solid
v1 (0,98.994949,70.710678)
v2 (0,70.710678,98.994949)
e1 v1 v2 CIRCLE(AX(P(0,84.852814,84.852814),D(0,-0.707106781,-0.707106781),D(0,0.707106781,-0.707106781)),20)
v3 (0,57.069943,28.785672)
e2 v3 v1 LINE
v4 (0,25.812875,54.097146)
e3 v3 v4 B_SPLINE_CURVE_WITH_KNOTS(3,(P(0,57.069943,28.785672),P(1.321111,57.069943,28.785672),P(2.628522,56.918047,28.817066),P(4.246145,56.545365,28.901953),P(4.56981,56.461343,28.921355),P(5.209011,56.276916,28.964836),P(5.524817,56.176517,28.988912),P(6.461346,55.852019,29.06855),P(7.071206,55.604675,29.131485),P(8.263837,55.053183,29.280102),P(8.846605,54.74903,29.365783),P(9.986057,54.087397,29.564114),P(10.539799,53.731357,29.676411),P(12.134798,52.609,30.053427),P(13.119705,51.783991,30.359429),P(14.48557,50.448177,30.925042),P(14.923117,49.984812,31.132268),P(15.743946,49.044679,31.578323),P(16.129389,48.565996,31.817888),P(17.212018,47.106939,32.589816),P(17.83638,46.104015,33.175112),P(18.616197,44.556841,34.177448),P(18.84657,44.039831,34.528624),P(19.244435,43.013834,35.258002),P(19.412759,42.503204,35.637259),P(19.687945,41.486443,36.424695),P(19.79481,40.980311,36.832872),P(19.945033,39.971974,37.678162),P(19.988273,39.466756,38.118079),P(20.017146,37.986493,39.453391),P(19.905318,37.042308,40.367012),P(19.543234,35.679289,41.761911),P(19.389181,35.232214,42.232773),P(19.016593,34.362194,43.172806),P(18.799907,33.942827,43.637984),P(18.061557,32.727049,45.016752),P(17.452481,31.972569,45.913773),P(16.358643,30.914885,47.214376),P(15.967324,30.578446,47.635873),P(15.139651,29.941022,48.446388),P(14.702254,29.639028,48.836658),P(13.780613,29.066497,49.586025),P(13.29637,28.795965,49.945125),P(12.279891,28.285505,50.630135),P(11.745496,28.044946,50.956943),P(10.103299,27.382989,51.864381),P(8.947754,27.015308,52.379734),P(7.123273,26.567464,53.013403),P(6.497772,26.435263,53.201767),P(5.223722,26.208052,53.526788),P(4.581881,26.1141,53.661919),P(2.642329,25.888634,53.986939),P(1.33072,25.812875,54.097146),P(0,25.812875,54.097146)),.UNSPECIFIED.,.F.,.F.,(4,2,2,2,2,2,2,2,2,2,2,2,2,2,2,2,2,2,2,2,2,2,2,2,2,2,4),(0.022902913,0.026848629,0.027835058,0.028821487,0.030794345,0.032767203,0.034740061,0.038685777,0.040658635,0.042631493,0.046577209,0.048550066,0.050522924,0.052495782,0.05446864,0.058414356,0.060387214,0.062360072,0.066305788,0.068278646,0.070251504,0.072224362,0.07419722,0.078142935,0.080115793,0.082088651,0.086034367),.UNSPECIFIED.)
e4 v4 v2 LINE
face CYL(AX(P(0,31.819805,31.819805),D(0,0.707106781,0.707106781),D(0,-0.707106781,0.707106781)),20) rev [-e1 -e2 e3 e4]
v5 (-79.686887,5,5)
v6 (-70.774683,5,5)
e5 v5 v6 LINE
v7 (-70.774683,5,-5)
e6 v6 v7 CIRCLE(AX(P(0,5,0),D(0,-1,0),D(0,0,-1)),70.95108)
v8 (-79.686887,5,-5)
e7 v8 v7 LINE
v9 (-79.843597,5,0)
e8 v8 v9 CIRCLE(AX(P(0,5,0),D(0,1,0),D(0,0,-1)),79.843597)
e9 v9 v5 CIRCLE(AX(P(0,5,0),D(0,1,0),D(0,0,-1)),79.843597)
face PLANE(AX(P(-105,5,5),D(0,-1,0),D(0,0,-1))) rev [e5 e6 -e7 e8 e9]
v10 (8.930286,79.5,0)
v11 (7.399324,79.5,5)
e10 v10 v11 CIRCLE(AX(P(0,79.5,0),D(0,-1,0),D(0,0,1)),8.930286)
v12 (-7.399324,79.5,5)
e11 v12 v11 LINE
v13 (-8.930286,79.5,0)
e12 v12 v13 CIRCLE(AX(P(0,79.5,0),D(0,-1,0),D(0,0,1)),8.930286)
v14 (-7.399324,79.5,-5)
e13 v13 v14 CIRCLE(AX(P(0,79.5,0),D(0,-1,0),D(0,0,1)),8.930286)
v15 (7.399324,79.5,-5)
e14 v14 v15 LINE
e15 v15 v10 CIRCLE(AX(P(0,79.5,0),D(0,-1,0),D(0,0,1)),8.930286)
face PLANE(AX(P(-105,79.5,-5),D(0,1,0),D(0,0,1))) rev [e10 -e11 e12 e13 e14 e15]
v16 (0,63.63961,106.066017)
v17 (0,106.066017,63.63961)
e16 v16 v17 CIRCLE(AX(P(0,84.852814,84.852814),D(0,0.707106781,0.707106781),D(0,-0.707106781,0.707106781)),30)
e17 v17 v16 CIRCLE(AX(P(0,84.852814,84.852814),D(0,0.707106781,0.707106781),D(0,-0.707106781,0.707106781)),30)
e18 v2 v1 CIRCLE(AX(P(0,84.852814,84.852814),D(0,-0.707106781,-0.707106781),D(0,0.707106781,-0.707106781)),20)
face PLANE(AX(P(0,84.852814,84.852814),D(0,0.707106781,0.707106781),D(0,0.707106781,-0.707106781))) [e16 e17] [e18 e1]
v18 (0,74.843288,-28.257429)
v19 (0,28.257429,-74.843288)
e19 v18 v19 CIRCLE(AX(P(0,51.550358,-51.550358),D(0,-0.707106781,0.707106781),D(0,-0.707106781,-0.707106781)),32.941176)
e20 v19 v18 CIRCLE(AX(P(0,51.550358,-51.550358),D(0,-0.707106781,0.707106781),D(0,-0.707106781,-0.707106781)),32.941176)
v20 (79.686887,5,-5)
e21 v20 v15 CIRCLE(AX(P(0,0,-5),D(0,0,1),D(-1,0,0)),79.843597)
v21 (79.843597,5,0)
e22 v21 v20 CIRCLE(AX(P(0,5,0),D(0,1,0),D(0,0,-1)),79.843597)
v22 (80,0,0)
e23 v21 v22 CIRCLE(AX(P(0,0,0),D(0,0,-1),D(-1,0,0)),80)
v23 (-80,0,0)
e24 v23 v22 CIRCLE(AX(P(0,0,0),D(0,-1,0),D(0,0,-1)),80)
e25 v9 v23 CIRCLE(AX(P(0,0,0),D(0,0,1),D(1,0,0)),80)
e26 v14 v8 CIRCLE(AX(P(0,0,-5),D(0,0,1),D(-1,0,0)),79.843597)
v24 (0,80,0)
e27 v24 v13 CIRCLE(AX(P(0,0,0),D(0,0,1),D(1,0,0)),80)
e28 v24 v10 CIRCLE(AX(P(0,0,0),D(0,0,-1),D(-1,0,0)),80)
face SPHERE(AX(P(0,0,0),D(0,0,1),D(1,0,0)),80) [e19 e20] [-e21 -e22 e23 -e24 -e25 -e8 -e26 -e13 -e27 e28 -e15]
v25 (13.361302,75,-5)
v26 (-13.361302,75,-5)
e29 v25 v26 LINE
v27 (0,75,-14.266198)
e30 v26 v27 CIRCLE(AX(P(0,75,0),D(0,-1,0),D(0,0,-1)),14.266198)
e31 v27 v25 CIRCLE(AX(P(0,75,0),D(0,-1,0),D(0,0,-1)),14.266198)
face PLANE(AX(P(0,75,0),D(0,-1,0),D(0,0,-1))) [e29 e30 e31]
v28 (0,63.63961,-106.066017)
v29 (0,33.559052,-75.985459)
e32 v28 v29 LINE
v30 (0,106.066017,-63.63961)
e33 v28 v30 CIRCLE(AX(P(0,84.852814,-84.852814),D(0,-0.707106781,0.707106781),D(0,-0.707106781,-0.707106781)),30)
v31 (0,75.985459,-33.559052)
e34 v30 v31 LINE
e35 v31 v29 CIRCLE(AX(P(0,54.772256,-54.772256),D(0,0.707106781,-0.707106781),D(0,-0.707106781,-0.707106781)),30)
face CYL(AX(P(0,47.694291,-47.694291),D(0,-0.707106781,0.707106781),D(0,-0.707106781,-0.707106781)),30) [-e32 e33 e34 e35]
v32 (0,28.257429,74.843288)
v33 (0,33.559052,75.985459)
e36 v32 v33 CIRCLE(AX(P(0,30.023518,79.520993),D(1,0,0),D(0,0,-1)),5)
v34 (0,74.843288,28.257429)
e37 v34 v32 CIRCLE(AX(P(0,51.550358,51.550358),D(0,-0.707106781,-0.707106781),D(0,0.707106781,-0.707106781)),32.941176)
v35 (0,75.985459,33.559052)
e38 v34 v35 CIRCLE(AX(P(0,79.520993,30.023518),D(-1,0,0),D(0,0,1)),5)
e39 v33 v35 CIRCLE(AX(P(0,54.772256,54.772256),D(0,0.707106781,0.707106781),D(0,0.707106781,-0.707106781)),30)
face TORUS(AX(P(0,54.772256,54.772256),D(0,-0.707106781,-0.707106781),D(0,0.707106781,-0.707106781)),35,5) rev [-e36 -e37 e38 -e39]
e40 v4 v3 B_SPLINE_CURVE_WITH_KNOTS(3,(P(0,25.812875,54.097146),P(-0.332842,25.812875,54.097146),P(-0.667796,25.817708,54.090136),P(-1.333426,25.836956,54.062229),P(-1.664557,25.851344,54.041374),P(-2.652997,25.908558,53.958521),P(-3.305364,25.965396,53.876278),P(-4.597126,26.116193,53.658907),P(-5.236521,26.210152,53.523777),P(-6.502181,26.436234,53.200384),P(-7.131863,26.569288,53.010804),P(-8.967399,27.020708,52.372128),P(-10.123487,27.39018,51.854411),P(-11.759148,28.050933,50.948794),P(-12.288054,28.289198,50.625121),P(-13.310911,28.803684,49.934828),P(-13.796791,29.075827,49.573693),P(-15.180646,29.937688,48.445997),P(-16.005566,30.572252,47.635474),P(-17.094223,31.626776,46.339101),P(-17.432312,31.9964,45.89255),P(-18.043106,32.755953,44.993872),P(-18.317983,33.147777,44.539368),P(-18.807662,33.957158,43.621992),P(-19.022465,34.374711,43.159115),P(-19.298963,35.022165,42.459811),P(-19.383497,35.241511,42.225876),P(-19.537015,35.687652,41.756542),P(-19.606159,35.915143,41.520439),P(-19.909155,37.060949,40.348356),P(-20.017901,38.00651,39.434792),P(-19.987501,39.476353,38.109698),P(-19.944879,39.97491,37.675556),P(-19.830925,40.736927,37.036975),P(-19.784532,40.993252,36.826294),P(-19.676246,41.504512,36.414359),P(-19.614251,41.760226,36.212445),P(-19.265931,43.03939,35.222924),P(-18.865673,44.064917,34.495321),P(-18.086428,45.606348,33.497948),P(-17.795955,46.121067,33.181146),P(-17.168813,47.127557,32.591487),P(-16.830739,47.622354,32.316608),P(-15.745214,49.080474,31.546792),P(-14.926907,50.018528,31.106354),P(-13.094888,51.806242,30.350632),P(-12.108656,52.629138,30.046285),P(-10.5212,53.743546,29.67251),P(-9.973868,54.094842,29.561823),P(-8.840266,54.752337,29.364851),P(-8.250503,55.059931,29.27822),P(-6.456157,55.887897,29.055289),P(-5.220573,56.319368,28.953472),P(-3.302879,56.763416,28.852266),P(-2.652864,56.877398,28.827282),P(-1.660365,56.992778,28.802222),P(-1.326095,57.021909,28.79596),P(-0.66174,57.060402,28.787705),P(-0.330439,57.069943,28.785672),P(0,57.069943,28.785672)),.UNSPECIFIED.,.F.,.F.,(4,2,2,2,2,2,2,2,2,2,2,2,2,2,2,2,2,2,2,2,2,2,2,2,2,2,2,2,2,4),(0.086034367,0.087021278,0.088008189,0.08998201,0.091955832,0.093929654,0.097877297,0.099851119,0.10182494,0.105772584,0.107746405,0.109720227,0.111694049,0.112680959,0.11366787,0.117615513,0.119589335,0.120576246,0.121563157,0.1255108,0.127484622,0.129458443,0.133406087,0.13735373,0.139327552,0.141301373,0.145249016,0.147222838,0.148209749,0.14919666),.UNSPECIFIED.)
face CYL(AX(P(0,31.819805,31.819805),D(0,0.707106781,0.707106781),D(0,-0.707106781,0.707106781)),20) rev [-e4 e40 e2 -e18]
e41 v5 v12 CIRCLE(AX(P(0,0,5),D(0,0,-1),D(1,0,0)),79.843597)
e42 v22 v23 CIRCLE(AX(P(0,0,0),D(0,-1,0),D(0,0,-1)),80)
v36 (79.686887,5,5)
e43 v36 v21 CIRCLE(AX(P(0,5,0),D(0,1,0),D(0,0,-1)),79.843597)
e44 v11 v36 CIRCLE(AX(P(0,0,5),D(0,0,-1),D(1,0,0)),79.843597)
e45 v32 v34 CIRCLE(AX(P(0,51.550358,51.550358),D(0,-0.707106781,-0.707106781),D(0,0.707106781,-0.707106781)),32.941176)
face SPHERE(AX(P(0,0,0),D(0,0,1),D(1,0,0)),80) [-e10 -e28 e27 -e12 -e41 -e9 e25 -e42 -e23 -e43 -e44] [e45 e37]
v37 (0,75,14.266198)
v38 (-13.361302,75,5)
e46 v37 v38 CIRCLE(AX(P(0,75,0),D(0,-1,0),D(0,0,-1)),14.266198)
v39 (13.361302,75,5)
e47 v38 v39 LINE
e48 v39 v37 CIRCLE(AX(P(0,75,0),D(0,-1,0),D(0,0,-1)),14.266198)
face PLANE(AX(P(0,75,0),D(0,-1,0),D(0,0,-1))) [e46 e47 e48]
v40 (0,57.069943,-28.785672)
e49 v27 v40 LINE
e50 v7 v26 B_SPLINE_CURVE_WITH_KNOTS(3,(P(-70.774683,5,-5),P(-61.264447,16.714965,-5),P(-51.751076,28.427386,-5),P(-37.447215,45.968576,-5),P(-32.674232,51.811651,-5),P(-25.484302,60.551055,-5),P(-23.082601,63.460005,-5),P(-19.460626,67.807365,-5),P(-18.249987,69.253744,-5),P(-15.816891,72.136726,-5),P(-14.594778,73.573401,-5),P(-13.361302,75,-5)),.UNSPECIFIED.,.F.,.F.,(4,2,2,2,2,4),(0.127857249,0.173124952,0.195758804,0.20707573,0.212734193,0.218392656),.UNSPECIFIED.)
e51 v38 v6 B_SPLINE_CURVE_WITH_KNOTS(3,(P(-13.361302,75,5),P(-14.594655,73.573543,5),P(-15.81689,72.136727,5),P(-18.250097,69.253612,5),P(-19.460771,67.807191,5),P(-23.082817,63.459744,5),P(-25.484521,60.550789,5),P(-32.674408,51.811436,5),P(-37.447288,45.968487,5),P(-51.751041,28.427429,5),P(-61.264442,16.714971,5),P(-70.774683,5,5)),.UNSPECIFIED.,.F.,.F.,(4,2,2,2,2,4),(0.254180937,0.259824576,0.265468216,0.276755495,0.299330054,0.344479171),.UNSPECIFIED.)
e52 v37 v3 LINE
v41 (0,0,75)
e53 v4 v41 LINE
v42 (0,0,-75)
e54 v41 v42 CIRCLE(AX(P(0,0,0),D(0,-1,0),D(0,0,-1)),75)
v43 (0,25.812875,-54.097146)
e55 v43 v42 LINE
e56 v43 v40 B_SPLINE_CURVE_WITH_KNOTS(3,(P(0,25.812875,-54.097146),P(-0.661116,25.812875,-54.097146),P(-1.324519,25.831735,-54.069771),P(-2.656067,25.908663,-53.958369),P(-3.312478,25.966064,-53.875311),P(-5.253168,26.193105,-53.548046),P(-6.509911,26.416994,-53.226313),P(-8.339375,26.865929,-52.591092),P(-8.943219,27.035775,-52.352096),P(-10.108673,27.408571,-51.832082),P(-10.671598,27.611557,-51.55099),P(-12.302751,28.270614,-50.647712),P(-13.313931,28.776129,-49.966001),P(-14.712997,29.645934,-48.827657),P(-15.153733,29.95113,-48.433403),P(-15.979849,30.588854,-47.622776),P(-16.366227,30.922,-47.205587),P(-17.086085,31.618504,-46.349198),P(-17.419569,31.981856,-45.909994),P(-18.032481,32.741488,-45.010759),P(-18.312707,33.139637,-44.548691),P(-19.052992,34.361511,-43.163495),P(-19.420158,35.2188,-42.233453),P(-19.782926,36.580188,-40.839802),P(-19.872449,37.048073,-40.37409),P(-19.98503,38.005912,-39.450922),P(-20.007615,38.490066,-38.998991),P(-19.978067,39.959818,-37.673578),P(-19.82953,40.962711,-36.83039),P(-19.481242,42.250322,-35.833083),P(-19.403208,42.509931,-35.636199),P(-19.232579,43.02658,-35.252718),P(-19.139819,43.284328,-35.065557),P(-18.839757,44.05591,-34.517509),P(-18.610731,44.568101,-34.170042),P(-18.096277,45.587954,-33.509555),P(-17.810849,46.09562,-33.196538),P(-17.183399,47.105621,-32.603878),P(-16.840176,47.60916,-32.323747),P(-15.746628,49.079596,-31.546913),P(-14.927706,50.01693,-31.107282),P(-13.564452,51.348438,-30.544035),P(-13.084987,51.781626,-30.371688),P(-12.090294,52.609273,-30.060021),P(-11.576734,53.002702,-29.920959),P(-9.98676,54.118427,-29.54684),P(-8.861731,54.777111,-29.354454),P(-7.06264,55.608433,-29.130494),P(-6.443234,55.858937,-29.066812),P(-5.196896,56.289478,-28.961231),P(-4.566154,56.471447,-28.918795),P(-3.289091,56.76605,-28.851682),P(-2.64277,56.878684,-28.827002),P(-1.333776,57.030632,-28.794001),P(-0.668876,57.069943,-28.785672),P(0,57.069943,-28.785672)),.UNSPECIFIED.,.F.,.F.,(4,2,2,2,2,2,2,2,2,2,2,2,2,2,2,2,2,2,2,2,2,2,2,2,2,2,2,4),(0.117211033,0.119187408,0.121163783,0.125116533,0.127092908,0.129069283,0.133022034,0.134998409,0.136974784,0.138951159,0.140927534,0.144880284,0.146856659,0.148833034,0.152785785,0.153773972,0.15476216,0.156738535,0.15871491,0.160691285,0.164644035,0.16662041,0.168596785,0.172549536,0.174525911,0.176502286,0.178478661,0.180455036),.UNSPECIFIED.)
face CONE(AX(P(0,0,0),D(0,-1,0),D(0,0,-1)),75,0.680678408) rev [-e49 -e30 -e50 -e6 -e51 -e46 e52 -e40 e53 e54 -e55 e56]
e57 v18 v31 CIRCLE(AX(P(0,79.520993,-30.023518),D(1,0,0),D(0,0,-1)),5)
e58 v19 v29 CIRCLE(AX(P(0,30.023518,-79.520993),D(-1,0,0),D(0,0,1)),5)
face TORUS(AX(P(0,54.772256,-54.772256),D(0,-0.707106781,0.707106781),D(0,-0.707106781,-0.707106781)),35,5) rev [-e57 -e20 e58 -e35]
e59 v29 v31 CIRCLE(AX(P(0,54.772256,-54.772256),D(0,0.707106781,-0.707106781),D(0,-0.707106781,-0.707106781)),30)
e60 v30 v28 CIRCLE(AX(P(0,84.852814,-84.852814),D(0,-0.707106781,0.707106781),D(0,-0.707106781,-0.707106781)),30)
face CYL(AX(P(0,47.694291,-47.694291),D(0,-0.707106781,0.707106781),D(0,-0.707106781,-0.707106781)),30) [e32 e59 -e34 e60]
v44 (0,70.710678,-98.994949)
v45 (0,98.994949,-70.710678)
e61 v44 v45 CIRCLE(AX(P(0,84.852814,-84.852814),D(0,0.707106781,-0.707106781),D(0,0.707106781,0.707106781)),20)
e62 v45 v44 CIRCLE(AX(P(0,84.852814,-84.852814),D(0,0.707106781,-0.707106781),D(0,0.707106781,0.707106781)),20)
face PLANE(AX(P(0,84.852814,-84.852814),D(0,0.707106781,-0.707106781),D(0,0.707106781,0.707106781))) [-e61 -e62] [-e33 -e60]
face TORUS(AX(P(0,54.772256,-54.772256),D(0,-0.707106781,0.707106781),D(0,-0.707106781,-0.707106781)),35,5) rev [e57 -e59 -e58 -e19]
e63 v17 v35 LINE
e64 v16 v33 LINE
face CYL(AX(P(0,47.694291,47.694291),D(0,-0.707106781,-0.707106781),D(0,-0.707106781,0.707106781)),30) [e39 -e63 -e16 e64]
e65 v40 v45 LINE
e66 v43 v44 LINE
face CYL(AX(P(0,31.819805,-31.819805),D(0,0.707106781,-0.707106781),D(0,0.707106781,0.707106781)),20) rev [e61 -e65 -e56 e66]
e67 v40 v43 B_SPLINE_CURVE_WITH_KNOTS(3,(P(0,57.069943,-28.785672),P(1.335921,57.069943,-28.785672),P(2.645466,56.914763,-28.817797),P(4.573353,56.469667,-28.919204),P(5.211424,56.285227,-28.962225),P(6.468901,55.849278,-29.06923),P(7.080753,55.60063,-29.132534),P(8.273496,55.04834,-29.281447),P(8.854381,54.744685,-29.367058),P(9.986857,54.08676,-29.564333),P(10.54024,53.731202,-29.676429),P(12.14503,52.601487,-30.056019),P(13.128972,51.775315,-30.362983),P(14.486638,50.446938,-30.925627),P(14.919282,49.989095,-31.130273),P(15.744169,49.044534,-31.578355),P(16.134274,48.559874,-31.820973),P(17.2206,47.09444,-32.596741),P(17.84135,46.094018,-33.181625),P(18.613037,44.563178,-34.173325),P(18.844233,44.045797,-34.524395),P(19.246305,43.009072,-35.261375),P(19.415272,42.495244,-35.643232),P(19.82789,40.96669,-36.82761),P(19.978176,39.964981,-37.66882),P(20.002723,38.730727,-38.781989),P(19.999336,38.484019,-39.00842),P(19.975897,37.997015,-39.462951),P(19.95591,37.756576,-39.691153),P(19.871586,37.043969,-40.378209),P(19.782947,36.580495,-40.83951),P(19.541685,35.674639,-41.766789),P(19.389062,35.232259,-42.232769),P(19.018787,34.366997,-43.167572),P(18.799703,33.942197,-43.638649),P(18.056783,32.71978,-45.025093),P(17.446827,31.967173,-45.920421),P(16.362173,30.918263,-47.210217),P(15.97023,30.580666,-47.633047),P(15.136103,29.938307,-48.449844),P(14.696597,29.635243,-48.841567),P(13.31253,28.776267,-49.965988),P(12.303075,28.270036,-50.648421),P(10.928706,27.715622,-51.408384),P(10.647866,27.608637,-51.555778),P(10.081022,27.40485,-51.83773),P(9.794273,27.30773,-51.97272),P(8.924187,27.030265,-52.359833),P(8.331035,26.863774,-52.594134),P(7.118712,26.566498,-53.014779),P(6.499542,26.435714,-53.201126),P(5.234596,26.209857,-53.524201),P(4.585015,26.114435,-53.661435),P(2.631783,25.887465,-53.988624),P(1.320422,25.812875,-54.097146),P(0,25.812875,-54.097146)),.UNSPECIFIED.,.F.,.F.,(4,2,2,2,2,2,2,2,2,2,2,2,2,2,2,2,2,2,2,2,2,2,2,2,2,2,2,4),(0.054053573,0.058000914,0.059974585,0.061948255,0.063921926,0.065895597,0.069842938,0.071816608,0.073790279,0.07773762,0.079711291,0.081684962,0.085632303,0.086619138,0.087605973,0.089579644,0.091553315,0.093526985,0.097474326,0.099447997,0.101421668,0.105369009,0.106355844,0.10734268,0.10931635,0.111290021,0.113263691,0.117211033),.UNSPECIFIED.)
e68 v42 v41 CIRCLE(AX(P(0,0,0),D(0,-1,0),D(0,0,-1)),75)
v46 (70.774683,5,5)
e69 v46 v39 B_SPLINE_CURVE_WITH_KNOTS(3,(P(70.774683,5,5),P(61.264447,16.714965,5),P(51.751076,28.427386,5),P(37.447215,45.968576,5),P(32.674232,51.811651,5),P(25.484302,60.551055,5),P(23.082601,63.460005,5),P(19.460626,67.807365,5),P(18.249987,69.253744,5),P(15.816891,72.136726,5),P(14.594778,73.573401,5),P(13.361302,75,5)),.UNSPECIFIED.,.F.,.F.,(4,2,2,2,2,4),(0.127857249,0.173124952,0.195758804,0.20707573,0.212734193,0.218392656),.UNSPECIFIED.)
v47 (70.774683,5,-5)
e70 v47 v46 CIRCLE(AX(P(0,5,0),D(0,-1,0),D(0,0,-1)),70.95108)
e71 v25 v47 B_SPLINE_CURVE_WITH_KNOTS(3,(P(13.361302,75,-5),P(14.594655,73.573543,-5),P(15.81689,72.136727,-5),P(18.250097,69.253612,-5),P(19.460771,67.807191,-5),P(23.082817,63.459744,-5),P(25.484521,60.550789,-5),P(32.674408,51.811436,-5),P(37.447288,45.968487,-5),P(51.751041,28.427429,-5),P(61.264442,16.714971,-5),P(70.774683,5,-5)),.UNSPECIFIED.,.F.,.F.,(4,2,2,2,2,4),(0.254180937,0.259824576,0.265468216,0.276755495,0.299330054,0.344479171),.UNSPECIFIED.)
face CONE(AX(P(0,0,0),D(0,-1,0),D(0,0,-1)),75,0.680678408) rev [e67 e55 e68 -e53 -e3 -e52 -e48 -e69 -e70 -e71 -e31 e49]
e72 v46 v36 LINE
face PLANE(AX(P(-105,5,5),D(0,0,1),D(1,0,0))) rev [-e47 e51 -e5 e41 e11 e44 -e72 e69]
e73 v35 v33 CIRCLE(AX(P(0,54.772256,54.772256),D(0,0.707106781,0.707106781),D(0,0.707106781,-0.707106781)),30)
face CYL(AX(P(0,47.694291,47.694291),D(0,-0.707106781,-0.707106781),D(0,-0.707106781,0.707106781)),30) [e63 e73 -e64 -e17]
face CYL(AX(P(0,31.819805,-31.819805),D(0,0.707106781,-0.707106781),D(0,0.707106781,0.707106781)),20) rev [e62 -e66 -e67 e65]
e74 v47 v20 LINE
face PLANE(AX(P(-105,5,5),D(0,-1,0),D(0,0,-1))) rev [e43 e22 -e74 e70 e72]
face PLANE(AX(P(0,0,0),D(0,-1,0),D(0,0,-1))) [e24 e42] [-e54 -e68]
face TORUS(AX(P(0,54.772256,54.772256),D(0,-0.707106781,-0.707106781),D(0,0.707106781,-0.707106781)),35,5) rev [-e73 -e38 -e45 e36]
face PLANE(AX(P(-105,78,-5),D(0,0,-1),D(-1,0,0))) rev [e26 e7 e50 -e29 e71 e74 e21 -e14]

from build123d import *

# Parameters (mm, degrees)
DOME_SLOT_CUT_DEPTH = 105
ANGLED_CUT_SKETCH_R = 75
ANGLED_CUT_DEPTH    = 75
ANGLED_CUT_DRAFT    = -39
TUBE_BORE_SKETCH_R  = 20
TUBE_BORE_CUT_DEPTH = 75
TUBE_FILLET_R5_R    = 5


with BuildPart() as part:
    # Dome Profile Sketch → Dome R80 (revolve)
    with BuildSketch(Plane.XY):
        with BuildLine():
            Line((0, 0), (0, 80))
            ThreePointArc((0, 80), (56.568542495, 56.568542495), (80, 0))
            Line((80, 0), (0, 0))
        make_face()
    revolve(axis=Axis((0, 0, 0), (0, 1, 0)))

    # Dome Slot Sketch → Dome Slot Cut (cut, symmetric)
    with BuildSketch(Plane(origin=(0, 0, 0), x_dir=(0, 0, -1), z_dir=(1, 0, 0))):
        Polygon((5, 75), (5, 5), (-5, 5), (-5, 75), (-5, 78), (-5, 79), (-5, 79.5), (5, 79.5), (5, 78), align=None)
    extrude(amount=DOME_SLOT_CUT_DEPTH, both=True, mode=Mode.SUBTRACT)


with BuildPart() as angled_cut_tool:
    # Angled Cut Sketch → Angled Cut (with draft: the straight prism first)
    with BuildSketch(Plane.XZ):
        Circle(ANGLED_CUT_SKETCH_R)
    extrude(amount=-ANGLED_CUT_DEPTH)
    # Angled Cut: the draft: its side faces are tilted about the plane it starts from
    angled_cut_sides = [angled_cut_tool.faces().sort_by_distance(p)[0] for p in [
        (-75, 37.5, 0),
    ]]
    draft(angled_cut_sides, Plane.XZ, ANGLED_CUT_DRAFT)


with BuildPart() as part_1:
    add(part.part)

    # Angled Cut: cut by angled_cut_tool
    add(angled_cut_tool.part, mode=Mode.SUBTRACT)

    # Tube Boss Profile Sketch → Tube Boss (revolve)
    with BuildSketch(Plane(origin=(0, 0, 0), x_dir=(0, 0, -1), z_dir=(1, 0, 0))):
        Polygon((47.694291303, 47.694291303), (84.852813742, 84.852813742), (106.066017178, 63.639610307), (68.907494738, 26.481087867), (50.800202422, 44.588380184), align=None)
    tube_boss = revolve(axis=Axis((0, 47.694291303, -47.694291303), (0, 0.7071067811865478, -0.7071067811865474)))

    # Tube Bore Sketch → Tube Bore Cut (cut)
    with BuildSketch(Plane(origin=(0, 84.852813742, -84.852813742), x_dir=(1, 0, 0), z_dir=(0, 0.7071067811865477, -0.7071067811865475))):
        with Locations(Location((0, 0, 0), (0, 0, 270))):
            Circle(TUBE_BORE_SKETCH_R)
    tube_bore_cut = extrude(amount=-TUBE_BORE_CUT_DEPTH, mode=Mode.SUBTRACT)

    # Tube Bore Mirror: Tube Boss, Tube Bore Cut across plane
    add(tube_boss.mirror(Plane.XY))
    add(tube_bore_cut.mirror(Plane.XY), mode=Mode.SUBTRACT)

    # Tube Fillet R5
    tube_fillet_r5_edges = [part_1.edges().sort_by_distance(p)[0] for p in [
        (0, 73.653645844, -31.227238973),
        (0, 73.653645844, 31.227238973),
    ]]
    fillet(tube_fillet_r5_edges, radius=TUBE_FILLET_R5_R)


solid = part_1.part
